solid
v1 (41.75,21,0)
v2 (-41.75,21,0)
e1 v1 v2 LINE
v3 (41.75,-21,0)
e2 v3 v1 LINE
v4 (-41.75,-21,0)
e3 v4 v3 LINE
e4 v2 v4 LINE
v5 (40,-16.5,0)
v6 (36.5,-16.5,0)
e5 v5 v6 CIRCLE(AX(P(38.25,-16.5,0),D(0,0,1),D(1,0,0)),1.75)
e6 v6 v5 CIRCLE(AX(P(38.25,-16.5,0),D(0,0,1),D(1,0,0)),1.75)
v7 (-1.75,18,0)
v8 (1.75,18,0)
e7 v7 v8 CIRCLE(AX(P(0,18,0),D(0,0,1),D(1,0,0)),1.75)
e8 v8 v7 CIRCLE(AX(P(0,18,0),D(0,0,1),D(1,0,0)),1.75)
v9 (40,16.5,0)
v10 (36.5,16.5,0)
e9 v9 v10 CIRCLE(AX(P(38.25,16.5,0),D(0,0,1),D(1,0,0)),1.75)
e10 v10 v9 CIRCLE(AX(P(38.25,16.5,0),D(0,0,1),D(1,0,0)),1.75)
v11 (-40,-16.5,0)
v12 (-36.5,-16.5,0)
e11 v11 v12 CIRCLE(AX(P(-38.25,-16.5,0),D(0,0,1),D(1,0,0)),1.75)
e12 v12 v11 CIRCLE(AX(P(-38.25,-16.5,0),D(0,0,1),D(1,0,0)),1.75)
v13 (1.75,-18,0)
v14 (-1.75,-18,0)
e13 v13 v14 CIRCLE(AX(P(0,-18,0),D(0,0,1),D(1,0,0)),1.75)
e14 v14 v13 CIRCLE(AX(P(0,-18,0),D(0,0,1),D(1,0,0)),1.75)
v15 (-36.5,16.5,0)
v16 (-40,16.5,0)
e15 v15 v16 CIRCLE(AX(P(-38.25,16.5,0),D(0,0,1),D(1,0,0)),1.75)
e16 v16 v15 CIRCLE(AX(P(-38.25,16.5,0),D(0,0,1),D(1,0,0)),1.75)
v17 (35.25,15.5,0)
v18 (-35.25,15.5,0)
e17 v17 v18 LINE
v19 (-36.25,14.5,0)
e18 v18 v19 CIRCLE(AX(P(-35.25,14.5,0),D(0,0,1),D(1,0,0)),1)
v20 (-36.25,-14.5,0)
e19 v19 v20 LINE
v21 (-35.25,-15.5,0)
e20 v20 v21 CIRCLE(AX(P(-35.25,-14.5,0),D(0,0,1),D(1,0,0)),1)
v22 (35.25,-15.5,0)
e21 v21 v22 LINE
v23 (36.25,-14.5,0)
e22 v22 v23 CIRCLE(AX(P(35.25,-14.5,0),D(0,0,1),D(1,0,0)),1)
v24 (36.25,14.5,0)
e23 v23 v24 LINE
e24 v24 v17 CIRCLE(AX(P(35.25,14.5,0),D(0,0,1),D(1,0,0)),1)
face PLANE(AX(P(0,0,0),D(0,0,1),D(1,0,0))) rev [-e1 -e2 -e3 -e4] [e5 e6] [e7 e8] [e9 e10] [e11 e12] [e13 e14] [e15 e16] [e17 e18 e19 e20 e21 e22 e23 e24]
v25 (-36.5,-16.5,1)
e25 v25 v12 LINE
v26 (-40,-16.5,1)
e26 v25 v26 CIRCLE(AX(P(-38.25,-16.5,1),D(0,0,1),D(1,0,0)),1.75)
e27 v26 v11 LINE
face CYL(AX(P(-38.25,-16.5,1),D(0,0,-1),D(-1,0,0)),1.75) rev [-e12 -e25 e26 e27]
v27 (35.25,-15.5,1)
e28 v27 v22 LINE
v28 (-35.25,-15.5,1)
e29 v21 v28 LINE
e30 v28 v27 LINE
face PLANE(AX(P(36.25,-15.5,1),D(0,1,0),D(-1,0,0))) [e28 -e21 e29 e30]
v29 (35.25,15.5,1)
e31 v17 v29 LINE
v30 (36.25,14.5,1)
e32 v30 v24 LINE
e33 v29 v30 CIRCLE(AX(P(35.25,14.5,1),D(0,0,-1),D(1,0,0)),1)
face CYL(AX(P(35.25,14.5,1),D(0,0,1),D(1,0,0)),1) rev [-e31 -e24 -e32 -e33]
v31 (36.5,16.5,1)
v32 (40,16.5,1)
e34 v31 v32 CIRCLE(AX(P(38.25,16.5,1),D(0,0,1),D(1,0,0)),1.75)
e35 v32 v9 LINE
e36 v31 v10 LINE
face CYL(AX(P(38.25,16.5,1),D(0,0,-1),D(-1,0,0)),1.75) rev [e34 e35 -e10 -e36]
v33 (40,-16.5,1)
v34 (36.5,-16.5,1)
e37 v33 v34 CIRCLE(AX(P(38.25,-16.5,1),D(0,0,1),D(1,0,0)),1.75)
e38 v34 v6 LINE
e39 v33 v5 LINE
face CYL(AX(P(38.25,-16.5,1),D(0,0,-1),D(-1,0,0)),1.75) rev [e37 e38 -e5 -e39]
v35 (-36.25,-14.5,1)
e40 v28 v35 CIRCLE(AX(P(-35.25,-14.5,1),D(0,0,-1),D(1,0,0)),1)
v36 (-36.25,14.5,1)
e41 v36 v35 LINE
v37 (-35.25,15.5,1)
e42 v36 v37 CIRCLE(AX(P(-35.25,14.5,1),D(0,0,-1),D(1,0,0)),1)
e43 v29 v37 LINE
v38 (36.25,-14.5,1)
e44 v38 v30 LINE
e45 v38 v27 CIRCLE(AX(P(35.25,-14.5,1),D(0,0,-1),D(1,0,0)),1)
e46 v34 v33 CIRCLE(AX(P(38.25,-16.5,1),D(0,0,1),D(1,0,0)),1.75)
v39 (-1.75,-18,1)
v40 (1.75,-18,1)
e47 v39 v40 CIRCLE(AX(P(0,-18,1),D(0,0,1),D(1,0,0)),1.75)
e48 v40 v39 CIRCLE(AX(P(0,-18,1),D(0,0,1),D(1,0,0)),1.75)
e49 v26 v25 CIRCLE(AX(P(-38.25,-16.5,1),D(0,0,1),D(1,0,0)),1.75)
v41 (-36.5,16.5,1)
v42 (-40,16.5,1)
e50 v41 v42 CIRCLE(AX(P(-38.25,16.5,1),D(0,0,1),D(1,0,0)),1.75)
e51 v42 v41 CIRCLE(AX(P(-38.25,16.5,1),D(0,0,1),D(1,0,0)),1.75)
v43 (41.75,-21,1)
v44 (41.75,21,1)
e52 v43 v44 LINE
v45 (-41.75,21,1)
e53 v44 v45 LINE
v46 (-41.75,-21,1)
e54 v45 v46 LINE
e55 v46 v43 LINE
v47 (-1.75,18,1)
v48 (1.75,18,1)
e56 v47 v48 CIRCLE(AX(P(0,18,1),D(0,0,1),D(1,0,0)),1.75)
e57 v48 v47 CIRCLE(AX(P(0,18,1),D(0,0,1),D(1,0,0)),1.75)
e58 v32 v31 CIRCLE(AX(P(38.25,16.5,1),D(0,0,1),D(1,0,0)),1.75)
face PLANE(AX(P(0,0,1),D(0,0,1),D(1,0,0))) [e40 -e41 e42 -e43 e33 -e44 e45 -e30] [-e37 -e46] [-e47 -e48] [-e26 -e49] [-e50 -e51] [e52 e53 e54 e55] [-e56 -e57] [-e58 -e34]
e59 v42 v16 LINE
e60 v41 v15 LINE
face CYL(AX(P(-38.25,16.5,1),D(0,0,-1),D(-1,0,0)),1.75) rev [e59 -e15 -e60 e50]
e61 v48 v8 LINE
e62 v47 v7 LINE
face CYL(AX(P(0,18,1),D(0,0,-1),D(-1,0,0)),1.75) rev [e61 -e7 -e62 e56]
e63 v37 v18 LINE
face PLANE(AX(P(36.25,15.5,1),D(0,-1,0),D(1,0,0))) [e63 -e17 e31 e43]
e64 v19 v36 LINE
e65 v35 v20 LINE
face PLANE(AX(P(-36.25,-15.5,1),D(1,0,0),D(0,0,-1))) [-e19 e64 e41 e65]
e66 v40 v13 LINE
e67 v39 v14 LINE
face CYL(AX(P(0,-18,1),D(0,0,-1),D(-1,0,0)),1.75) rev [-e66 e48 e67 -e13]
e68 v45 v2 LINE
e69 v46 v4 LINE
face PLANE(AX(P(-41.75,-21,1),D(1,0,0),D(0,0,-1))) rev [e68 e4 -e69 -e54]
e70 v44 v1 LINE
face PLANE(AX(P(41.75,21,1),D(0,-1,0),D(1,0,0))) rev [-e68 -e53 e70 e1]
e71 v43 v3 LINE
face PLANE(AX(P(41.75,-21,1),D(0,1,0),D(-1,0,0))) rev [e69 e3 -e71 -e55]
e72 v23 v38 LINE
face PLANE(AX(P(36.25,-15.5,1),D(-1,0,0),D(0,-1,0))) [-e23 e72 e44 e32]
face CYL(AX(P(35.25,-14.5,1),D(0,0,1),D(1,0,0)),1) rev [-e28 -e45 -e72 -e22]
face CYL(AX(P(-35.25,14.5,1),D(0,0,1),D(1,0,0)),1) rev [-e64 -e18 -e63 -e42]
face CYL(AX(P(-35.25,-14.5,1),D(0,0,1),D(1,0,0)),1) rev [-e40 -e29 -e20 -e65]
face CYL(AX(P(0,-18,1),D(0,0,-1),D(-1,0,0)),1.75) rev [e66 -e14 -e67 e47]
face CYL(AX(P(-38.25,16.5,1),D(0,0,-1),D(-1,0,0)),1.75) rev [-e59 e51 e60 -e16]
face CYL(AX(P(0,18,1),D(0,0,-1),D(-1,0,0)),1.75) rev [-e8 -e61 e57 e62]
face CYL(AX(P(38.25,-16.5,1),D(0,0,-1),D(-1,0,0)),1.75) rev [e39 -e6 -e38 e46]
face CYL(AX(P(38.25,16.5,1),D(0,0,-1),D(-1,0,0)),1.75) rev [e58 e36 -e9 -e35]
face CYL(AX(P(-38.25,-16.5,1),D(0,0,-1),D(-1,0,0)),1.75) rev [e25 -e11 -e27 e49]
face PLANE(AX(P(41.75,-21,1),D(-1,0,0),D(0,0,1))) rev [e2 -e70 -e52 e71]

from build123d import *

# Parameters (mm, degrees)
SKETCH1_W           = 83.5
SKETCH1_H           = 42
SKETCH1_R           = 1.75
SKETCH1_W_2         = 72.5
SKETCH1_H_2         = 31
BOSS_EXTRUDE1_DEPTH = 1
FILLET1_R           = 1


with BuildPart() as part:
    # Sketch1 → Boss-Extrude1 (new body)
    with BuildSketch(Plane.XY):
        Rectangle(SKETCH1_W, SKETCH1_H)
        with Locations((-38.25, 16.5)):
            Circle(SKETCH1_R, mode=Mode.SUBTRACT)
        with Locations((38.25, 16.5)):
            Circle(SKETCH1_R, mode=Mode.SUBTRACT)
        with Locations((38.25, -16.5)):
            Circle(SKETCH1_R, mode=Mode.SUBTRACT)
        with Locations((-38.25, -16.5)):
            Circle(SKETCH1_R, mode=Mode.SUBTRACT)
        with Locations((0, 18)):
            Circle(SKETCH1_R, mode=Mode.SUBTRACT)
        with Locations((0, -18)):
            Circle(SKETCH1_R, mode=Mode.SUBTRACT)
        Rectangle(SKETCH1_W_2, SKETCH1_H_2, mode=Mode.SUBTRACT)
    extrude(amount=BOSS_EXTRUDE1_DEPTH)

    # Fillet1
    fillet1_edges = [part.edges().sort_by_distance(p)[0] for p in [
        (-36.25, 15.5, 0.5),
        (-36.25, -15.5, 0.5),
        (36.25, -15.5, 0.5),
        (36.25, 15.5, 0.5),
    ]]
    fillet(fillet1_edges, radius=FILLET1_R)


solid = part.part
